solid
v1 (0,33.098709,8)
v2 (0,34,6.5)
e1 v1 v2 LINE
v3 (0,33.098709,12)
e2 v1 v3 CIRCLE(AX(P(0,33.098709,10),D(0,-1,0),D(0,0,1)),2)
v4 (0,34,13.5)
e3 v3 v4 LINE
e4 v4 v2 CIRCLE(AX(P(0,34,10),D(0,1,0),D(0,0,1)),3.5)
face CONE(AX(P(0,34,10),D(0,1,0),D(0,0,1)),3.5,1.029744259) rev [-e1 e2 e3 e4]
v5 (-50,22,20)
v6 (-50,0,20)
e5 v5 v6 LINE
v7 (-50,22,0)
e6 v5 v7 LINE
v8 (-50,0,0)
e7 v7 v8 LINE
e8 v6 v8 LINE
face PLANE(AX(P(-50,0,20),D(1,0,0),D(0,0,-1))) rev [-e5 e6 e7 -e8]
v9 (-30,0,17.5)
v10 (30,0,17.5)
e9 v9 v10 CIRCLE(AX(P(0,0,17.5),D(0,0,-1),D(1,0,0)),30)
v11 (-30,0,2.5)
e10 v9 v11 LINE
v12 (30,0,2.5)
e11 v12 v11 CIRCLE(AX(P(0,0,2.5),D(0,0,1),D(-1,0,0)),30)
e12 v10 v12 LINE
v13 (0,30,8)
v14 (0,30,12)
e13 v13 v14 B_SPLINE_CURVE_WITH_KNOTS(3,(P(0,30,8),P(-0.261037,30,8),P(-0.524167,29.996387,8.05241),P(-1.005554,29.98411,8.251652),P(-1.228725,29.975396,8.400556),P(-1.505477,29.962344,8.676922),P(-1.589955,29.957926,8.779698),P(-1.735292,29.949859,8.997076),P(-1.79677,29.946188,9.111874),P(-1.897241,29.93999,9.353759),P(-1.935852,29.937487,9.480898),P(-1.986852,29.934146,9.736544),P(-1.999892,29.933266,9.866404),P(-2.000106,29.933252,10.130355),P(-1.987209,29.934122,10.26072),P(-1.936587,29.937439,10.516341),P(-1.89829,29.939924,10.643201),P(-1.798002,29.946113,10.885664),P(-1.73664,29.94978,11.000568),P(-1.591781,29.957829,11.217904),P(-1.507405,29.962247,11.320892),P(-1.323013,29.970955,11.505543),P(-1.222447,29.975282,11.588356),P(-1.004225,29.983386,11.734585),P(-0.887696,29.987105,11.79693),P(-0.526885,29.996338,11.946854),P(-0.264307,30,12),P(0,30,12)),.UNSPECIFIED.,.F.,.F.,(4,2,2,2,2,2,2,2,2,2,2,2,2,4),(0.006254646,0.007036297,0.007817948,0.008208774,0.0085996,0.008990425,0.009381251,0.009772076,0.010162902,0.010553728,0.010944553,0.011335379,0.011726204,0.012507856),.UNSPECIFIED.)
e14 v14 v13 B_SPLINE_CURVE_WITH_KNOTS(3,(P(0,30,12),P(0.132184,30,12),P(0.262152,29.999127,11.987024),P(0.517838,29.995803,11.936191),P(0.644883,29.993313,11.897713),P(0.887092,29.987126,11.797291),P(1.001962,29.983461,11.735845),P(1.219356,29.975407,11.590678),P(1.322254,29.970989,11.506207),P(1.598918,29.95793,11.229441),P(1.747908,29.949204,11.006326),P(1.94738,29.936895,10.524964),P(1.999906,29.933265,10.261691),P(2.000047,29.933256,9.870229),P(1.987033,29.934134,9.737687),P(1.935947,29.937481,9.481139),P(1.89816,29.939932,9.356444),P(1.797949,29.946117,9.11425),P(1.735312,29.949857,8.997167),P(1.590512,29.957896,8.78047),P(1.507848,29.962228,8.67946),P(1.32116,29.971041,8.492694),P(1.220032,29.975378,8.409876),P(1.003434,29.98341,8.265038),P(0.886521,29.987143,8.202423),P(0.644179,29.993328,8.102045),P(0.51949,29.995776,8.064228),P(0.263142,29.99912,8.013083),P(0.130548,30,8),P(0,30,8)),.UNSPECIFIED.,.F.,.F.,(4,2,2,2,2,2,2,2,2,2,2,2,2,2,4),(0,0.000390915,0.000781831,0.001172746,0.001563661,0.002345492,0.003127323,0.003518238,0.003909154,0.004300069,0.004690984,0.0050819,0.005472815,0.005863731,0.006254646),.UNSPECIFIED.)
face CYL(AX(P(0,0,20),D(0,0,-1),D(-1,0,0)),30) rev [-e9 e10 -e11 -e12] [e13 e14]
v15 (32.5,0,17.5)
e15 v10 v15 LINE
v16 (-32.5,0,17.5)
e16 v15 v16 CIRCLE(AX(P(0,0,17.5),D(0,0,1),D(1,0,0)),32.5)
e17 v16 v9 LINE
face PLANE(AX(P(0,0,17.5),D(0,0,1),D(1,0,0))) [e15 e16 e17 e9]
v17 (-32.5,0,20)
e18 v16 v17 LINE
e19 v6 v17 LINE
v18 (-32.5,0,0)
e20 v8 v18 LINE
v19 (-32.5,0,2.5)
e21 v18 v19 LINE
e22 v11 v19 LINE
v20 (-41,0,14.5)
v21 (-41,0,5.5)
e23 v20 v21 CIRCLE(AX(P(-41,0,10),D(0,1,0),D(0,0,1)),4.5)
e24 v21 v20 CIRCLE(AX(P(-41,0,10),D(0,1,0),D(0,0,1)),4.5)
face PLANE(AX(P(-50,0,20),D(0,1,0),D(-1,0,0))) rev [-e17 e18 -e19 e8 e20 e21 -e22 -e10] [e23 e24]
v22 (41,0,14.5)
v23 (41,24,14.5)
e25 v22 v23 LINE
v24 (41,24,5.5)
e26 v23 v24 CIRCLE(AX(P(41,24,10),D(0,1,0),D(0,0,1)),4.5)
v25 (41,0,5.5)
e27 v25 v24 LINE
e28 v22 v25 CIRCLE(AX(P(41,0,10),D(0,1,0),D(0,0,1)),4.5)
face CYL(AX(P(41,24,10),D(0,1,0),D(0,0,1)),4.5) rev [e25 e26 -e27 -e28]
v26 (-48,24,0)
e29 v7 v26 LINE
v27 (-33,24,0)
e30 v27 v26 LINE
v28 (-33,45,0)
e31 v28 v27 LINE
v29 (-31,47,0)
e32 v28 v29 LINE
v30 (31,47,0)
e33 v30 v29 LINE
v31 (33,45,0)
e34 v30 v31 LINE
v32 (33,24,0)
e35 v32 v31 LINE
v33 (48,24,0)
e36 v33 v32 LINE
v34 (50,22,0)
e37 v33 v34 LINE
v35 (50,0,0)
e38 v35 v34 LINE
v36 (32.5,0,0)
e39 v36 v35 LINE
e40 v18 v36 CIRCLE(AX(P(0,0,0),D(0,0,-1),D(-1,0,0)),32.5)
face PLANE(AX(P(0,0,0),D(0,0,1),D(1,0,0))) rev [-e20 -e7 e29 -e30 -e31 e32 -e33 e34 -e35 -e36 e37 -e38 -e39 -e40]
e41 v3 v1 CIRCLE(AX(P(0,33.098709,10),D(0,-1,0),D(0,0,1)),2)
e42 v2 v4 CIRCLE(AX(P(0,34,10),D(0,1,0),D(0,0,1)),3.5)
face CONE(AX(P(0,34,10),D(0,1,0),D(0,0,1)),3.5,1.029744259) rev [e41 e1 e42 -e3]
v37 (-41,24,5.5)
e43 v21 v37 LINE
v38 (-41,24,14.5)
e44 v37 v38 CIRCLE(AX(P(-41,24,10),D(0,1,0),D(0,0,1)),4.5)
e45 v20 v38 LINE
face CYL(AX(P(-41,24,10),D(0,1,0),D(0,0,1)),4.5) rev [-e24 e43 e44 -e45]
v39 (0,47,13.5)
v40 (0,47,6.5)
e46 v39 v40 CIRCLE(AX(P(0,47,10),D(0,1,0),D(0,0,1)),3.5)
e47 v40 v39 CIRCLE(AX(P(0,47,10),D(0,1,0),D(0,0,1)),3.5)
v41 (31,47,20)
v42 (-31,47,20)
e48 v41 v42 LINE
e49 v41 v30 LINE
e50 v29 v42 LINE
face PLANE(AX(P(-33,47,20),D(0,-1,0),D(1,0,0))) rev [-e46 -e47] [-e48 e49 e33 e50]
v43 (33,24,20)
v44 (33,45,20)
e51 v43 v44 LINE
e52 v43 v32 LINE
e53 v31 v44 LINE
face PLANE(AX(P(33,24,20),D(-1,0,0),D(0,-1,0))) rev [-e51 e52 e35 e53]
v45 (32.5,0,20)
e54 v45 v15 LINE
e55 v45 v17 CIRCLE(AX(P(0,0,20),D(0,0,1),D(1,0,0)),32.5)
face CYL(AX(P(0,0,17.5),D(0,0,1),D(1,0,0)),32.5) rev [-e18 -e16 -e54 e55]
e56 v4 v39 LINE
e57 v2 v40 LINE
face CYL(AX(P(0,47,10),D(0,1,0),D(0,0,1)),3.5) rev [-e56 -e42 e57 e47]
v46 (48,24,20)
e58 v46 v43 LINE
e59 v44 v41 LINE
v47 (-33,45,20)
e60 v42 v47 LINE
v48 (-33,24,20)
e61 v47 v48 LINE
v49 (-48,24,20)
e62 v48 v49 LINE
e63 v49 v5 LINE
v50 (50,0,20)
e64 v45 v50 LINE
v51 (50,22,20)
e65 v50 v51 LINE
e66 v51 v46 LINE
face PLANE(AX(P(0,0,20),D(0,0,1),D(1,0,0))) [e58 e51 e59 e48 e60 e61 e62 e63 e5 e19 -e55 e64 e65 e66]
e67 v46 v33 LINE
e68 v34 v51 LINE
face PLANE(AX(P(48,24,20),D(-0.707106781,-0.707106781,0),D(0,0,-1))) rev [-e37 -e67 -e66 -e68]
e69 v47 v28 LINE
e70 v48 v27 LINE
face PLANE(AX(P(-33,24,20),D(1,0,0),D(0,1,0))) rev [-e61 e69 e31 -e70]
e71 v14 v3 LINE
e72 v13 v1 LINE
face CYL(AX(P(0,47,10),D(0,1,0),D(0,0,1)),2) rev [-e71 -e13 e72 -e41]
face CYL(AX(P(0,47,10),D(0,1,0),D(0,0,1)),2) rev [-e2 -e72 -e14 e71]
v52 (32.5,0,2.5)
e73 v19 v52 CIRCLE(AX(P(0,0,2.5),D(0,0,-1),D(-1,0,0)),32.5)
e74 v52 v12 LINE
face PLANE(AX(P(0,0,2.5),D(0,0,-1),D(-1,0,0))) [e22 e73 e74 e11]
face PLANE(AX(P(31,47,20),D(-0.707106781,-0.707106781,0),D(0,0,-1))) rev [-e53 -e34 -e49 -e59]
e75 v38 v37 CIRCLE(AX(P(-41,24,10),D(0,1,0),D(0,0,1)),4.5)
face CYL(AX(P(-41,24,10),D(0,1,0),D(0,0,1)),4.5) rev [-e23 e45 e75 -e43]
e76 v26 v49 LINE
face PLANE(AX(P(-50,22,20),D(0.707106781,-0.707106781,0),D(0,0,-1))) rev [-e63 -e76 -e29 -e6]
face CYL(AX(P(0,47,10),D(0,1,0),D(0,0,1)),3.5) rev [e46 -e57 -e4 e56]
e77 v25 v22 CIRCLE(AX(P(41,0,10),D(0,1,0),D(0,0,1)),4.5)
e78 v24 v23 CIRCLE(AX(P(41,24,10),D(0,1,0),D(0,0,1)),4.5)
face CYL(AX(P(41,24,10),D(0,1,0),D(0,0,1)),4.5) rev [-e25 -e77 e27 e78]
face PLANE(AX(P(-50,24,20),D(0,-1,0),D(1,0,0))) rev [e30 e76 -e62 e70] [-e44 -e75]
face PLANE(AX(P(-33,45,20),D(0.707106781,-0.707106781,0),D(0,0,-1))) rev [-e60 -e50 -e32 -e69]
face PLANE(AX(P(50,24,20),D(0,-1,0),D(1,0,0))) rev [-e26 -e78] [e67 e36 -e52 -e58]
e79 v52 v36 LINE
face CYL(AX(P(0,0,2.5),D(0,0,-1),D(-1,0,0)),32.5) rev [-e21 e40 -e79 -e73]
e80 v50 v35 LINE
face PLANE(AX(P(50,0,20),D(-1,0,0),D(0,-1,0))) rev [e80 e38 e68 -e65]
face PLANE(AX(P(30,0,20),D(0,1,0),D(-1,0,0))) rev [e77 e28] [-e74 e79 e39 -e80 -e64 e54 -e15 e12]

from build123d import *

# Parameters (mm, degrees)
BOSS_EXTRUDE1_DEPTH       = 20
CHAMFER1_SIZE             = 2
M8X1_0_TAPPED_HOLE1_D     = 7
M8X1_0_TAPPED_HOLE1_DEPTH = 13
M8X1_0_TAPPED_HOLE1_TIP   = 2.103012167
HOLE2_D                   = 9
SKETCH15_R                = 32.5
CUT_EXTRUDE3_DEPTH        = 2.5
CUT_EXTRUDE4_START        = -2.5
SKETCH16_R                = 32.5
CUT_EXTRUDE4_DEPTH        = 2.5
HOLE3_D                   = 4


with BuildPart() as part:
    # Sketch1 → Boss-Extrude1 (new body)
    with BuildSketch(Plane.XY):
        with BuildLine():
            Line((-50, 24), (-33, 24))
            Line((-33, 24), (-33, 47))
            Line((-33, 47), (33, 47))
            Line((33, 47), (33, 24))
            Line((33, 24), (50, 24))
            Line((50, 24), (50, 0))
            Line((50, 0), (30, 0))
            ThreePointArc((30, 0), (0, 30), (-30, 0))
            Line((-30, 0), (-50, 0))
            Line((-50, 0), (-50, 24))
        make_face()
    extrude(amount=BOSS_EXTRUDE1_DEPTH)

    # Chamfer1
    chamfer1_edges = [part.edges().sort_by_distance(p)[0] for p in [
        (-50, 24, 10),
        (-33, 47, 10),
        (33, 47, 10),
        (50, 24, 10),
    ]]
    chamfer(chamfer1_edges, length=CHAMFER1_SIZE)

    # M8x1.0 Tapped Hole1
    with Locations(Plane(origin=(0, 47, 0), x_dir=(1, 0, 0), z_dir=(0, 1, 0))):
        with Locations((0, -10)):
            Hole(M8X1_0_TAPPED_HOLE1_D / 2, depth=M8X1_0_TAPPED_HOLE1_DEPTH)
            with Locations((0, 0, -(M8X1_0_TAPPED_HOLE1_DEPTH + M8X1_0_TAPPED_HOLE1_TIP / 2))):  # 118° drill point
                Cone(0, M8X1_0_TAPPED_HOLE1_D / 2, M8X1_0_TAPPED_HOLE1_TIP, mode=Mode.SUBTRACT)

    # Hole2 (through all)
    with Locations(Plane(origin=(0, 24, 0), x_dir=(1, 0, 0), z_dir=(0, 1, 0))):
        with Locations((-41, -10), (41, -10)):
            Hole(HOLE2_D / 2)

    # Sketch15 → Cut-Extrude3 (cut)
    with BuildSketch(Plane(origin=(0, 0, 0), x_dir=(-1, 0, 0), z_dir=(0, 0, -1))):
        Circle(SKETCH15_R)
    extrude(amount=-CUT_EXTRUDE3_DEPTH, mode=Mode.SUBTRACT)

    # Sketch16 → Cut-Extrude4 (cut)
    with BuildSketch(Plane.XY.offset(20).offset(CUT_EXTRUDE4_START)):
        Circle(SKETCH16_R)
    extrude(amount=CUT_EXTRUDE4_DEPTH, mode=Mode.SUBTRACT)

    # Hole3 (through all)
    with Locations(Plane(origin=(0, 47, 0), x_dir=(1, 0, 0), z_dir=(0, 1, 0))):
        with Locations((0, -10)):
            Hole(HOLE3_D / 2)


solid = part.part
